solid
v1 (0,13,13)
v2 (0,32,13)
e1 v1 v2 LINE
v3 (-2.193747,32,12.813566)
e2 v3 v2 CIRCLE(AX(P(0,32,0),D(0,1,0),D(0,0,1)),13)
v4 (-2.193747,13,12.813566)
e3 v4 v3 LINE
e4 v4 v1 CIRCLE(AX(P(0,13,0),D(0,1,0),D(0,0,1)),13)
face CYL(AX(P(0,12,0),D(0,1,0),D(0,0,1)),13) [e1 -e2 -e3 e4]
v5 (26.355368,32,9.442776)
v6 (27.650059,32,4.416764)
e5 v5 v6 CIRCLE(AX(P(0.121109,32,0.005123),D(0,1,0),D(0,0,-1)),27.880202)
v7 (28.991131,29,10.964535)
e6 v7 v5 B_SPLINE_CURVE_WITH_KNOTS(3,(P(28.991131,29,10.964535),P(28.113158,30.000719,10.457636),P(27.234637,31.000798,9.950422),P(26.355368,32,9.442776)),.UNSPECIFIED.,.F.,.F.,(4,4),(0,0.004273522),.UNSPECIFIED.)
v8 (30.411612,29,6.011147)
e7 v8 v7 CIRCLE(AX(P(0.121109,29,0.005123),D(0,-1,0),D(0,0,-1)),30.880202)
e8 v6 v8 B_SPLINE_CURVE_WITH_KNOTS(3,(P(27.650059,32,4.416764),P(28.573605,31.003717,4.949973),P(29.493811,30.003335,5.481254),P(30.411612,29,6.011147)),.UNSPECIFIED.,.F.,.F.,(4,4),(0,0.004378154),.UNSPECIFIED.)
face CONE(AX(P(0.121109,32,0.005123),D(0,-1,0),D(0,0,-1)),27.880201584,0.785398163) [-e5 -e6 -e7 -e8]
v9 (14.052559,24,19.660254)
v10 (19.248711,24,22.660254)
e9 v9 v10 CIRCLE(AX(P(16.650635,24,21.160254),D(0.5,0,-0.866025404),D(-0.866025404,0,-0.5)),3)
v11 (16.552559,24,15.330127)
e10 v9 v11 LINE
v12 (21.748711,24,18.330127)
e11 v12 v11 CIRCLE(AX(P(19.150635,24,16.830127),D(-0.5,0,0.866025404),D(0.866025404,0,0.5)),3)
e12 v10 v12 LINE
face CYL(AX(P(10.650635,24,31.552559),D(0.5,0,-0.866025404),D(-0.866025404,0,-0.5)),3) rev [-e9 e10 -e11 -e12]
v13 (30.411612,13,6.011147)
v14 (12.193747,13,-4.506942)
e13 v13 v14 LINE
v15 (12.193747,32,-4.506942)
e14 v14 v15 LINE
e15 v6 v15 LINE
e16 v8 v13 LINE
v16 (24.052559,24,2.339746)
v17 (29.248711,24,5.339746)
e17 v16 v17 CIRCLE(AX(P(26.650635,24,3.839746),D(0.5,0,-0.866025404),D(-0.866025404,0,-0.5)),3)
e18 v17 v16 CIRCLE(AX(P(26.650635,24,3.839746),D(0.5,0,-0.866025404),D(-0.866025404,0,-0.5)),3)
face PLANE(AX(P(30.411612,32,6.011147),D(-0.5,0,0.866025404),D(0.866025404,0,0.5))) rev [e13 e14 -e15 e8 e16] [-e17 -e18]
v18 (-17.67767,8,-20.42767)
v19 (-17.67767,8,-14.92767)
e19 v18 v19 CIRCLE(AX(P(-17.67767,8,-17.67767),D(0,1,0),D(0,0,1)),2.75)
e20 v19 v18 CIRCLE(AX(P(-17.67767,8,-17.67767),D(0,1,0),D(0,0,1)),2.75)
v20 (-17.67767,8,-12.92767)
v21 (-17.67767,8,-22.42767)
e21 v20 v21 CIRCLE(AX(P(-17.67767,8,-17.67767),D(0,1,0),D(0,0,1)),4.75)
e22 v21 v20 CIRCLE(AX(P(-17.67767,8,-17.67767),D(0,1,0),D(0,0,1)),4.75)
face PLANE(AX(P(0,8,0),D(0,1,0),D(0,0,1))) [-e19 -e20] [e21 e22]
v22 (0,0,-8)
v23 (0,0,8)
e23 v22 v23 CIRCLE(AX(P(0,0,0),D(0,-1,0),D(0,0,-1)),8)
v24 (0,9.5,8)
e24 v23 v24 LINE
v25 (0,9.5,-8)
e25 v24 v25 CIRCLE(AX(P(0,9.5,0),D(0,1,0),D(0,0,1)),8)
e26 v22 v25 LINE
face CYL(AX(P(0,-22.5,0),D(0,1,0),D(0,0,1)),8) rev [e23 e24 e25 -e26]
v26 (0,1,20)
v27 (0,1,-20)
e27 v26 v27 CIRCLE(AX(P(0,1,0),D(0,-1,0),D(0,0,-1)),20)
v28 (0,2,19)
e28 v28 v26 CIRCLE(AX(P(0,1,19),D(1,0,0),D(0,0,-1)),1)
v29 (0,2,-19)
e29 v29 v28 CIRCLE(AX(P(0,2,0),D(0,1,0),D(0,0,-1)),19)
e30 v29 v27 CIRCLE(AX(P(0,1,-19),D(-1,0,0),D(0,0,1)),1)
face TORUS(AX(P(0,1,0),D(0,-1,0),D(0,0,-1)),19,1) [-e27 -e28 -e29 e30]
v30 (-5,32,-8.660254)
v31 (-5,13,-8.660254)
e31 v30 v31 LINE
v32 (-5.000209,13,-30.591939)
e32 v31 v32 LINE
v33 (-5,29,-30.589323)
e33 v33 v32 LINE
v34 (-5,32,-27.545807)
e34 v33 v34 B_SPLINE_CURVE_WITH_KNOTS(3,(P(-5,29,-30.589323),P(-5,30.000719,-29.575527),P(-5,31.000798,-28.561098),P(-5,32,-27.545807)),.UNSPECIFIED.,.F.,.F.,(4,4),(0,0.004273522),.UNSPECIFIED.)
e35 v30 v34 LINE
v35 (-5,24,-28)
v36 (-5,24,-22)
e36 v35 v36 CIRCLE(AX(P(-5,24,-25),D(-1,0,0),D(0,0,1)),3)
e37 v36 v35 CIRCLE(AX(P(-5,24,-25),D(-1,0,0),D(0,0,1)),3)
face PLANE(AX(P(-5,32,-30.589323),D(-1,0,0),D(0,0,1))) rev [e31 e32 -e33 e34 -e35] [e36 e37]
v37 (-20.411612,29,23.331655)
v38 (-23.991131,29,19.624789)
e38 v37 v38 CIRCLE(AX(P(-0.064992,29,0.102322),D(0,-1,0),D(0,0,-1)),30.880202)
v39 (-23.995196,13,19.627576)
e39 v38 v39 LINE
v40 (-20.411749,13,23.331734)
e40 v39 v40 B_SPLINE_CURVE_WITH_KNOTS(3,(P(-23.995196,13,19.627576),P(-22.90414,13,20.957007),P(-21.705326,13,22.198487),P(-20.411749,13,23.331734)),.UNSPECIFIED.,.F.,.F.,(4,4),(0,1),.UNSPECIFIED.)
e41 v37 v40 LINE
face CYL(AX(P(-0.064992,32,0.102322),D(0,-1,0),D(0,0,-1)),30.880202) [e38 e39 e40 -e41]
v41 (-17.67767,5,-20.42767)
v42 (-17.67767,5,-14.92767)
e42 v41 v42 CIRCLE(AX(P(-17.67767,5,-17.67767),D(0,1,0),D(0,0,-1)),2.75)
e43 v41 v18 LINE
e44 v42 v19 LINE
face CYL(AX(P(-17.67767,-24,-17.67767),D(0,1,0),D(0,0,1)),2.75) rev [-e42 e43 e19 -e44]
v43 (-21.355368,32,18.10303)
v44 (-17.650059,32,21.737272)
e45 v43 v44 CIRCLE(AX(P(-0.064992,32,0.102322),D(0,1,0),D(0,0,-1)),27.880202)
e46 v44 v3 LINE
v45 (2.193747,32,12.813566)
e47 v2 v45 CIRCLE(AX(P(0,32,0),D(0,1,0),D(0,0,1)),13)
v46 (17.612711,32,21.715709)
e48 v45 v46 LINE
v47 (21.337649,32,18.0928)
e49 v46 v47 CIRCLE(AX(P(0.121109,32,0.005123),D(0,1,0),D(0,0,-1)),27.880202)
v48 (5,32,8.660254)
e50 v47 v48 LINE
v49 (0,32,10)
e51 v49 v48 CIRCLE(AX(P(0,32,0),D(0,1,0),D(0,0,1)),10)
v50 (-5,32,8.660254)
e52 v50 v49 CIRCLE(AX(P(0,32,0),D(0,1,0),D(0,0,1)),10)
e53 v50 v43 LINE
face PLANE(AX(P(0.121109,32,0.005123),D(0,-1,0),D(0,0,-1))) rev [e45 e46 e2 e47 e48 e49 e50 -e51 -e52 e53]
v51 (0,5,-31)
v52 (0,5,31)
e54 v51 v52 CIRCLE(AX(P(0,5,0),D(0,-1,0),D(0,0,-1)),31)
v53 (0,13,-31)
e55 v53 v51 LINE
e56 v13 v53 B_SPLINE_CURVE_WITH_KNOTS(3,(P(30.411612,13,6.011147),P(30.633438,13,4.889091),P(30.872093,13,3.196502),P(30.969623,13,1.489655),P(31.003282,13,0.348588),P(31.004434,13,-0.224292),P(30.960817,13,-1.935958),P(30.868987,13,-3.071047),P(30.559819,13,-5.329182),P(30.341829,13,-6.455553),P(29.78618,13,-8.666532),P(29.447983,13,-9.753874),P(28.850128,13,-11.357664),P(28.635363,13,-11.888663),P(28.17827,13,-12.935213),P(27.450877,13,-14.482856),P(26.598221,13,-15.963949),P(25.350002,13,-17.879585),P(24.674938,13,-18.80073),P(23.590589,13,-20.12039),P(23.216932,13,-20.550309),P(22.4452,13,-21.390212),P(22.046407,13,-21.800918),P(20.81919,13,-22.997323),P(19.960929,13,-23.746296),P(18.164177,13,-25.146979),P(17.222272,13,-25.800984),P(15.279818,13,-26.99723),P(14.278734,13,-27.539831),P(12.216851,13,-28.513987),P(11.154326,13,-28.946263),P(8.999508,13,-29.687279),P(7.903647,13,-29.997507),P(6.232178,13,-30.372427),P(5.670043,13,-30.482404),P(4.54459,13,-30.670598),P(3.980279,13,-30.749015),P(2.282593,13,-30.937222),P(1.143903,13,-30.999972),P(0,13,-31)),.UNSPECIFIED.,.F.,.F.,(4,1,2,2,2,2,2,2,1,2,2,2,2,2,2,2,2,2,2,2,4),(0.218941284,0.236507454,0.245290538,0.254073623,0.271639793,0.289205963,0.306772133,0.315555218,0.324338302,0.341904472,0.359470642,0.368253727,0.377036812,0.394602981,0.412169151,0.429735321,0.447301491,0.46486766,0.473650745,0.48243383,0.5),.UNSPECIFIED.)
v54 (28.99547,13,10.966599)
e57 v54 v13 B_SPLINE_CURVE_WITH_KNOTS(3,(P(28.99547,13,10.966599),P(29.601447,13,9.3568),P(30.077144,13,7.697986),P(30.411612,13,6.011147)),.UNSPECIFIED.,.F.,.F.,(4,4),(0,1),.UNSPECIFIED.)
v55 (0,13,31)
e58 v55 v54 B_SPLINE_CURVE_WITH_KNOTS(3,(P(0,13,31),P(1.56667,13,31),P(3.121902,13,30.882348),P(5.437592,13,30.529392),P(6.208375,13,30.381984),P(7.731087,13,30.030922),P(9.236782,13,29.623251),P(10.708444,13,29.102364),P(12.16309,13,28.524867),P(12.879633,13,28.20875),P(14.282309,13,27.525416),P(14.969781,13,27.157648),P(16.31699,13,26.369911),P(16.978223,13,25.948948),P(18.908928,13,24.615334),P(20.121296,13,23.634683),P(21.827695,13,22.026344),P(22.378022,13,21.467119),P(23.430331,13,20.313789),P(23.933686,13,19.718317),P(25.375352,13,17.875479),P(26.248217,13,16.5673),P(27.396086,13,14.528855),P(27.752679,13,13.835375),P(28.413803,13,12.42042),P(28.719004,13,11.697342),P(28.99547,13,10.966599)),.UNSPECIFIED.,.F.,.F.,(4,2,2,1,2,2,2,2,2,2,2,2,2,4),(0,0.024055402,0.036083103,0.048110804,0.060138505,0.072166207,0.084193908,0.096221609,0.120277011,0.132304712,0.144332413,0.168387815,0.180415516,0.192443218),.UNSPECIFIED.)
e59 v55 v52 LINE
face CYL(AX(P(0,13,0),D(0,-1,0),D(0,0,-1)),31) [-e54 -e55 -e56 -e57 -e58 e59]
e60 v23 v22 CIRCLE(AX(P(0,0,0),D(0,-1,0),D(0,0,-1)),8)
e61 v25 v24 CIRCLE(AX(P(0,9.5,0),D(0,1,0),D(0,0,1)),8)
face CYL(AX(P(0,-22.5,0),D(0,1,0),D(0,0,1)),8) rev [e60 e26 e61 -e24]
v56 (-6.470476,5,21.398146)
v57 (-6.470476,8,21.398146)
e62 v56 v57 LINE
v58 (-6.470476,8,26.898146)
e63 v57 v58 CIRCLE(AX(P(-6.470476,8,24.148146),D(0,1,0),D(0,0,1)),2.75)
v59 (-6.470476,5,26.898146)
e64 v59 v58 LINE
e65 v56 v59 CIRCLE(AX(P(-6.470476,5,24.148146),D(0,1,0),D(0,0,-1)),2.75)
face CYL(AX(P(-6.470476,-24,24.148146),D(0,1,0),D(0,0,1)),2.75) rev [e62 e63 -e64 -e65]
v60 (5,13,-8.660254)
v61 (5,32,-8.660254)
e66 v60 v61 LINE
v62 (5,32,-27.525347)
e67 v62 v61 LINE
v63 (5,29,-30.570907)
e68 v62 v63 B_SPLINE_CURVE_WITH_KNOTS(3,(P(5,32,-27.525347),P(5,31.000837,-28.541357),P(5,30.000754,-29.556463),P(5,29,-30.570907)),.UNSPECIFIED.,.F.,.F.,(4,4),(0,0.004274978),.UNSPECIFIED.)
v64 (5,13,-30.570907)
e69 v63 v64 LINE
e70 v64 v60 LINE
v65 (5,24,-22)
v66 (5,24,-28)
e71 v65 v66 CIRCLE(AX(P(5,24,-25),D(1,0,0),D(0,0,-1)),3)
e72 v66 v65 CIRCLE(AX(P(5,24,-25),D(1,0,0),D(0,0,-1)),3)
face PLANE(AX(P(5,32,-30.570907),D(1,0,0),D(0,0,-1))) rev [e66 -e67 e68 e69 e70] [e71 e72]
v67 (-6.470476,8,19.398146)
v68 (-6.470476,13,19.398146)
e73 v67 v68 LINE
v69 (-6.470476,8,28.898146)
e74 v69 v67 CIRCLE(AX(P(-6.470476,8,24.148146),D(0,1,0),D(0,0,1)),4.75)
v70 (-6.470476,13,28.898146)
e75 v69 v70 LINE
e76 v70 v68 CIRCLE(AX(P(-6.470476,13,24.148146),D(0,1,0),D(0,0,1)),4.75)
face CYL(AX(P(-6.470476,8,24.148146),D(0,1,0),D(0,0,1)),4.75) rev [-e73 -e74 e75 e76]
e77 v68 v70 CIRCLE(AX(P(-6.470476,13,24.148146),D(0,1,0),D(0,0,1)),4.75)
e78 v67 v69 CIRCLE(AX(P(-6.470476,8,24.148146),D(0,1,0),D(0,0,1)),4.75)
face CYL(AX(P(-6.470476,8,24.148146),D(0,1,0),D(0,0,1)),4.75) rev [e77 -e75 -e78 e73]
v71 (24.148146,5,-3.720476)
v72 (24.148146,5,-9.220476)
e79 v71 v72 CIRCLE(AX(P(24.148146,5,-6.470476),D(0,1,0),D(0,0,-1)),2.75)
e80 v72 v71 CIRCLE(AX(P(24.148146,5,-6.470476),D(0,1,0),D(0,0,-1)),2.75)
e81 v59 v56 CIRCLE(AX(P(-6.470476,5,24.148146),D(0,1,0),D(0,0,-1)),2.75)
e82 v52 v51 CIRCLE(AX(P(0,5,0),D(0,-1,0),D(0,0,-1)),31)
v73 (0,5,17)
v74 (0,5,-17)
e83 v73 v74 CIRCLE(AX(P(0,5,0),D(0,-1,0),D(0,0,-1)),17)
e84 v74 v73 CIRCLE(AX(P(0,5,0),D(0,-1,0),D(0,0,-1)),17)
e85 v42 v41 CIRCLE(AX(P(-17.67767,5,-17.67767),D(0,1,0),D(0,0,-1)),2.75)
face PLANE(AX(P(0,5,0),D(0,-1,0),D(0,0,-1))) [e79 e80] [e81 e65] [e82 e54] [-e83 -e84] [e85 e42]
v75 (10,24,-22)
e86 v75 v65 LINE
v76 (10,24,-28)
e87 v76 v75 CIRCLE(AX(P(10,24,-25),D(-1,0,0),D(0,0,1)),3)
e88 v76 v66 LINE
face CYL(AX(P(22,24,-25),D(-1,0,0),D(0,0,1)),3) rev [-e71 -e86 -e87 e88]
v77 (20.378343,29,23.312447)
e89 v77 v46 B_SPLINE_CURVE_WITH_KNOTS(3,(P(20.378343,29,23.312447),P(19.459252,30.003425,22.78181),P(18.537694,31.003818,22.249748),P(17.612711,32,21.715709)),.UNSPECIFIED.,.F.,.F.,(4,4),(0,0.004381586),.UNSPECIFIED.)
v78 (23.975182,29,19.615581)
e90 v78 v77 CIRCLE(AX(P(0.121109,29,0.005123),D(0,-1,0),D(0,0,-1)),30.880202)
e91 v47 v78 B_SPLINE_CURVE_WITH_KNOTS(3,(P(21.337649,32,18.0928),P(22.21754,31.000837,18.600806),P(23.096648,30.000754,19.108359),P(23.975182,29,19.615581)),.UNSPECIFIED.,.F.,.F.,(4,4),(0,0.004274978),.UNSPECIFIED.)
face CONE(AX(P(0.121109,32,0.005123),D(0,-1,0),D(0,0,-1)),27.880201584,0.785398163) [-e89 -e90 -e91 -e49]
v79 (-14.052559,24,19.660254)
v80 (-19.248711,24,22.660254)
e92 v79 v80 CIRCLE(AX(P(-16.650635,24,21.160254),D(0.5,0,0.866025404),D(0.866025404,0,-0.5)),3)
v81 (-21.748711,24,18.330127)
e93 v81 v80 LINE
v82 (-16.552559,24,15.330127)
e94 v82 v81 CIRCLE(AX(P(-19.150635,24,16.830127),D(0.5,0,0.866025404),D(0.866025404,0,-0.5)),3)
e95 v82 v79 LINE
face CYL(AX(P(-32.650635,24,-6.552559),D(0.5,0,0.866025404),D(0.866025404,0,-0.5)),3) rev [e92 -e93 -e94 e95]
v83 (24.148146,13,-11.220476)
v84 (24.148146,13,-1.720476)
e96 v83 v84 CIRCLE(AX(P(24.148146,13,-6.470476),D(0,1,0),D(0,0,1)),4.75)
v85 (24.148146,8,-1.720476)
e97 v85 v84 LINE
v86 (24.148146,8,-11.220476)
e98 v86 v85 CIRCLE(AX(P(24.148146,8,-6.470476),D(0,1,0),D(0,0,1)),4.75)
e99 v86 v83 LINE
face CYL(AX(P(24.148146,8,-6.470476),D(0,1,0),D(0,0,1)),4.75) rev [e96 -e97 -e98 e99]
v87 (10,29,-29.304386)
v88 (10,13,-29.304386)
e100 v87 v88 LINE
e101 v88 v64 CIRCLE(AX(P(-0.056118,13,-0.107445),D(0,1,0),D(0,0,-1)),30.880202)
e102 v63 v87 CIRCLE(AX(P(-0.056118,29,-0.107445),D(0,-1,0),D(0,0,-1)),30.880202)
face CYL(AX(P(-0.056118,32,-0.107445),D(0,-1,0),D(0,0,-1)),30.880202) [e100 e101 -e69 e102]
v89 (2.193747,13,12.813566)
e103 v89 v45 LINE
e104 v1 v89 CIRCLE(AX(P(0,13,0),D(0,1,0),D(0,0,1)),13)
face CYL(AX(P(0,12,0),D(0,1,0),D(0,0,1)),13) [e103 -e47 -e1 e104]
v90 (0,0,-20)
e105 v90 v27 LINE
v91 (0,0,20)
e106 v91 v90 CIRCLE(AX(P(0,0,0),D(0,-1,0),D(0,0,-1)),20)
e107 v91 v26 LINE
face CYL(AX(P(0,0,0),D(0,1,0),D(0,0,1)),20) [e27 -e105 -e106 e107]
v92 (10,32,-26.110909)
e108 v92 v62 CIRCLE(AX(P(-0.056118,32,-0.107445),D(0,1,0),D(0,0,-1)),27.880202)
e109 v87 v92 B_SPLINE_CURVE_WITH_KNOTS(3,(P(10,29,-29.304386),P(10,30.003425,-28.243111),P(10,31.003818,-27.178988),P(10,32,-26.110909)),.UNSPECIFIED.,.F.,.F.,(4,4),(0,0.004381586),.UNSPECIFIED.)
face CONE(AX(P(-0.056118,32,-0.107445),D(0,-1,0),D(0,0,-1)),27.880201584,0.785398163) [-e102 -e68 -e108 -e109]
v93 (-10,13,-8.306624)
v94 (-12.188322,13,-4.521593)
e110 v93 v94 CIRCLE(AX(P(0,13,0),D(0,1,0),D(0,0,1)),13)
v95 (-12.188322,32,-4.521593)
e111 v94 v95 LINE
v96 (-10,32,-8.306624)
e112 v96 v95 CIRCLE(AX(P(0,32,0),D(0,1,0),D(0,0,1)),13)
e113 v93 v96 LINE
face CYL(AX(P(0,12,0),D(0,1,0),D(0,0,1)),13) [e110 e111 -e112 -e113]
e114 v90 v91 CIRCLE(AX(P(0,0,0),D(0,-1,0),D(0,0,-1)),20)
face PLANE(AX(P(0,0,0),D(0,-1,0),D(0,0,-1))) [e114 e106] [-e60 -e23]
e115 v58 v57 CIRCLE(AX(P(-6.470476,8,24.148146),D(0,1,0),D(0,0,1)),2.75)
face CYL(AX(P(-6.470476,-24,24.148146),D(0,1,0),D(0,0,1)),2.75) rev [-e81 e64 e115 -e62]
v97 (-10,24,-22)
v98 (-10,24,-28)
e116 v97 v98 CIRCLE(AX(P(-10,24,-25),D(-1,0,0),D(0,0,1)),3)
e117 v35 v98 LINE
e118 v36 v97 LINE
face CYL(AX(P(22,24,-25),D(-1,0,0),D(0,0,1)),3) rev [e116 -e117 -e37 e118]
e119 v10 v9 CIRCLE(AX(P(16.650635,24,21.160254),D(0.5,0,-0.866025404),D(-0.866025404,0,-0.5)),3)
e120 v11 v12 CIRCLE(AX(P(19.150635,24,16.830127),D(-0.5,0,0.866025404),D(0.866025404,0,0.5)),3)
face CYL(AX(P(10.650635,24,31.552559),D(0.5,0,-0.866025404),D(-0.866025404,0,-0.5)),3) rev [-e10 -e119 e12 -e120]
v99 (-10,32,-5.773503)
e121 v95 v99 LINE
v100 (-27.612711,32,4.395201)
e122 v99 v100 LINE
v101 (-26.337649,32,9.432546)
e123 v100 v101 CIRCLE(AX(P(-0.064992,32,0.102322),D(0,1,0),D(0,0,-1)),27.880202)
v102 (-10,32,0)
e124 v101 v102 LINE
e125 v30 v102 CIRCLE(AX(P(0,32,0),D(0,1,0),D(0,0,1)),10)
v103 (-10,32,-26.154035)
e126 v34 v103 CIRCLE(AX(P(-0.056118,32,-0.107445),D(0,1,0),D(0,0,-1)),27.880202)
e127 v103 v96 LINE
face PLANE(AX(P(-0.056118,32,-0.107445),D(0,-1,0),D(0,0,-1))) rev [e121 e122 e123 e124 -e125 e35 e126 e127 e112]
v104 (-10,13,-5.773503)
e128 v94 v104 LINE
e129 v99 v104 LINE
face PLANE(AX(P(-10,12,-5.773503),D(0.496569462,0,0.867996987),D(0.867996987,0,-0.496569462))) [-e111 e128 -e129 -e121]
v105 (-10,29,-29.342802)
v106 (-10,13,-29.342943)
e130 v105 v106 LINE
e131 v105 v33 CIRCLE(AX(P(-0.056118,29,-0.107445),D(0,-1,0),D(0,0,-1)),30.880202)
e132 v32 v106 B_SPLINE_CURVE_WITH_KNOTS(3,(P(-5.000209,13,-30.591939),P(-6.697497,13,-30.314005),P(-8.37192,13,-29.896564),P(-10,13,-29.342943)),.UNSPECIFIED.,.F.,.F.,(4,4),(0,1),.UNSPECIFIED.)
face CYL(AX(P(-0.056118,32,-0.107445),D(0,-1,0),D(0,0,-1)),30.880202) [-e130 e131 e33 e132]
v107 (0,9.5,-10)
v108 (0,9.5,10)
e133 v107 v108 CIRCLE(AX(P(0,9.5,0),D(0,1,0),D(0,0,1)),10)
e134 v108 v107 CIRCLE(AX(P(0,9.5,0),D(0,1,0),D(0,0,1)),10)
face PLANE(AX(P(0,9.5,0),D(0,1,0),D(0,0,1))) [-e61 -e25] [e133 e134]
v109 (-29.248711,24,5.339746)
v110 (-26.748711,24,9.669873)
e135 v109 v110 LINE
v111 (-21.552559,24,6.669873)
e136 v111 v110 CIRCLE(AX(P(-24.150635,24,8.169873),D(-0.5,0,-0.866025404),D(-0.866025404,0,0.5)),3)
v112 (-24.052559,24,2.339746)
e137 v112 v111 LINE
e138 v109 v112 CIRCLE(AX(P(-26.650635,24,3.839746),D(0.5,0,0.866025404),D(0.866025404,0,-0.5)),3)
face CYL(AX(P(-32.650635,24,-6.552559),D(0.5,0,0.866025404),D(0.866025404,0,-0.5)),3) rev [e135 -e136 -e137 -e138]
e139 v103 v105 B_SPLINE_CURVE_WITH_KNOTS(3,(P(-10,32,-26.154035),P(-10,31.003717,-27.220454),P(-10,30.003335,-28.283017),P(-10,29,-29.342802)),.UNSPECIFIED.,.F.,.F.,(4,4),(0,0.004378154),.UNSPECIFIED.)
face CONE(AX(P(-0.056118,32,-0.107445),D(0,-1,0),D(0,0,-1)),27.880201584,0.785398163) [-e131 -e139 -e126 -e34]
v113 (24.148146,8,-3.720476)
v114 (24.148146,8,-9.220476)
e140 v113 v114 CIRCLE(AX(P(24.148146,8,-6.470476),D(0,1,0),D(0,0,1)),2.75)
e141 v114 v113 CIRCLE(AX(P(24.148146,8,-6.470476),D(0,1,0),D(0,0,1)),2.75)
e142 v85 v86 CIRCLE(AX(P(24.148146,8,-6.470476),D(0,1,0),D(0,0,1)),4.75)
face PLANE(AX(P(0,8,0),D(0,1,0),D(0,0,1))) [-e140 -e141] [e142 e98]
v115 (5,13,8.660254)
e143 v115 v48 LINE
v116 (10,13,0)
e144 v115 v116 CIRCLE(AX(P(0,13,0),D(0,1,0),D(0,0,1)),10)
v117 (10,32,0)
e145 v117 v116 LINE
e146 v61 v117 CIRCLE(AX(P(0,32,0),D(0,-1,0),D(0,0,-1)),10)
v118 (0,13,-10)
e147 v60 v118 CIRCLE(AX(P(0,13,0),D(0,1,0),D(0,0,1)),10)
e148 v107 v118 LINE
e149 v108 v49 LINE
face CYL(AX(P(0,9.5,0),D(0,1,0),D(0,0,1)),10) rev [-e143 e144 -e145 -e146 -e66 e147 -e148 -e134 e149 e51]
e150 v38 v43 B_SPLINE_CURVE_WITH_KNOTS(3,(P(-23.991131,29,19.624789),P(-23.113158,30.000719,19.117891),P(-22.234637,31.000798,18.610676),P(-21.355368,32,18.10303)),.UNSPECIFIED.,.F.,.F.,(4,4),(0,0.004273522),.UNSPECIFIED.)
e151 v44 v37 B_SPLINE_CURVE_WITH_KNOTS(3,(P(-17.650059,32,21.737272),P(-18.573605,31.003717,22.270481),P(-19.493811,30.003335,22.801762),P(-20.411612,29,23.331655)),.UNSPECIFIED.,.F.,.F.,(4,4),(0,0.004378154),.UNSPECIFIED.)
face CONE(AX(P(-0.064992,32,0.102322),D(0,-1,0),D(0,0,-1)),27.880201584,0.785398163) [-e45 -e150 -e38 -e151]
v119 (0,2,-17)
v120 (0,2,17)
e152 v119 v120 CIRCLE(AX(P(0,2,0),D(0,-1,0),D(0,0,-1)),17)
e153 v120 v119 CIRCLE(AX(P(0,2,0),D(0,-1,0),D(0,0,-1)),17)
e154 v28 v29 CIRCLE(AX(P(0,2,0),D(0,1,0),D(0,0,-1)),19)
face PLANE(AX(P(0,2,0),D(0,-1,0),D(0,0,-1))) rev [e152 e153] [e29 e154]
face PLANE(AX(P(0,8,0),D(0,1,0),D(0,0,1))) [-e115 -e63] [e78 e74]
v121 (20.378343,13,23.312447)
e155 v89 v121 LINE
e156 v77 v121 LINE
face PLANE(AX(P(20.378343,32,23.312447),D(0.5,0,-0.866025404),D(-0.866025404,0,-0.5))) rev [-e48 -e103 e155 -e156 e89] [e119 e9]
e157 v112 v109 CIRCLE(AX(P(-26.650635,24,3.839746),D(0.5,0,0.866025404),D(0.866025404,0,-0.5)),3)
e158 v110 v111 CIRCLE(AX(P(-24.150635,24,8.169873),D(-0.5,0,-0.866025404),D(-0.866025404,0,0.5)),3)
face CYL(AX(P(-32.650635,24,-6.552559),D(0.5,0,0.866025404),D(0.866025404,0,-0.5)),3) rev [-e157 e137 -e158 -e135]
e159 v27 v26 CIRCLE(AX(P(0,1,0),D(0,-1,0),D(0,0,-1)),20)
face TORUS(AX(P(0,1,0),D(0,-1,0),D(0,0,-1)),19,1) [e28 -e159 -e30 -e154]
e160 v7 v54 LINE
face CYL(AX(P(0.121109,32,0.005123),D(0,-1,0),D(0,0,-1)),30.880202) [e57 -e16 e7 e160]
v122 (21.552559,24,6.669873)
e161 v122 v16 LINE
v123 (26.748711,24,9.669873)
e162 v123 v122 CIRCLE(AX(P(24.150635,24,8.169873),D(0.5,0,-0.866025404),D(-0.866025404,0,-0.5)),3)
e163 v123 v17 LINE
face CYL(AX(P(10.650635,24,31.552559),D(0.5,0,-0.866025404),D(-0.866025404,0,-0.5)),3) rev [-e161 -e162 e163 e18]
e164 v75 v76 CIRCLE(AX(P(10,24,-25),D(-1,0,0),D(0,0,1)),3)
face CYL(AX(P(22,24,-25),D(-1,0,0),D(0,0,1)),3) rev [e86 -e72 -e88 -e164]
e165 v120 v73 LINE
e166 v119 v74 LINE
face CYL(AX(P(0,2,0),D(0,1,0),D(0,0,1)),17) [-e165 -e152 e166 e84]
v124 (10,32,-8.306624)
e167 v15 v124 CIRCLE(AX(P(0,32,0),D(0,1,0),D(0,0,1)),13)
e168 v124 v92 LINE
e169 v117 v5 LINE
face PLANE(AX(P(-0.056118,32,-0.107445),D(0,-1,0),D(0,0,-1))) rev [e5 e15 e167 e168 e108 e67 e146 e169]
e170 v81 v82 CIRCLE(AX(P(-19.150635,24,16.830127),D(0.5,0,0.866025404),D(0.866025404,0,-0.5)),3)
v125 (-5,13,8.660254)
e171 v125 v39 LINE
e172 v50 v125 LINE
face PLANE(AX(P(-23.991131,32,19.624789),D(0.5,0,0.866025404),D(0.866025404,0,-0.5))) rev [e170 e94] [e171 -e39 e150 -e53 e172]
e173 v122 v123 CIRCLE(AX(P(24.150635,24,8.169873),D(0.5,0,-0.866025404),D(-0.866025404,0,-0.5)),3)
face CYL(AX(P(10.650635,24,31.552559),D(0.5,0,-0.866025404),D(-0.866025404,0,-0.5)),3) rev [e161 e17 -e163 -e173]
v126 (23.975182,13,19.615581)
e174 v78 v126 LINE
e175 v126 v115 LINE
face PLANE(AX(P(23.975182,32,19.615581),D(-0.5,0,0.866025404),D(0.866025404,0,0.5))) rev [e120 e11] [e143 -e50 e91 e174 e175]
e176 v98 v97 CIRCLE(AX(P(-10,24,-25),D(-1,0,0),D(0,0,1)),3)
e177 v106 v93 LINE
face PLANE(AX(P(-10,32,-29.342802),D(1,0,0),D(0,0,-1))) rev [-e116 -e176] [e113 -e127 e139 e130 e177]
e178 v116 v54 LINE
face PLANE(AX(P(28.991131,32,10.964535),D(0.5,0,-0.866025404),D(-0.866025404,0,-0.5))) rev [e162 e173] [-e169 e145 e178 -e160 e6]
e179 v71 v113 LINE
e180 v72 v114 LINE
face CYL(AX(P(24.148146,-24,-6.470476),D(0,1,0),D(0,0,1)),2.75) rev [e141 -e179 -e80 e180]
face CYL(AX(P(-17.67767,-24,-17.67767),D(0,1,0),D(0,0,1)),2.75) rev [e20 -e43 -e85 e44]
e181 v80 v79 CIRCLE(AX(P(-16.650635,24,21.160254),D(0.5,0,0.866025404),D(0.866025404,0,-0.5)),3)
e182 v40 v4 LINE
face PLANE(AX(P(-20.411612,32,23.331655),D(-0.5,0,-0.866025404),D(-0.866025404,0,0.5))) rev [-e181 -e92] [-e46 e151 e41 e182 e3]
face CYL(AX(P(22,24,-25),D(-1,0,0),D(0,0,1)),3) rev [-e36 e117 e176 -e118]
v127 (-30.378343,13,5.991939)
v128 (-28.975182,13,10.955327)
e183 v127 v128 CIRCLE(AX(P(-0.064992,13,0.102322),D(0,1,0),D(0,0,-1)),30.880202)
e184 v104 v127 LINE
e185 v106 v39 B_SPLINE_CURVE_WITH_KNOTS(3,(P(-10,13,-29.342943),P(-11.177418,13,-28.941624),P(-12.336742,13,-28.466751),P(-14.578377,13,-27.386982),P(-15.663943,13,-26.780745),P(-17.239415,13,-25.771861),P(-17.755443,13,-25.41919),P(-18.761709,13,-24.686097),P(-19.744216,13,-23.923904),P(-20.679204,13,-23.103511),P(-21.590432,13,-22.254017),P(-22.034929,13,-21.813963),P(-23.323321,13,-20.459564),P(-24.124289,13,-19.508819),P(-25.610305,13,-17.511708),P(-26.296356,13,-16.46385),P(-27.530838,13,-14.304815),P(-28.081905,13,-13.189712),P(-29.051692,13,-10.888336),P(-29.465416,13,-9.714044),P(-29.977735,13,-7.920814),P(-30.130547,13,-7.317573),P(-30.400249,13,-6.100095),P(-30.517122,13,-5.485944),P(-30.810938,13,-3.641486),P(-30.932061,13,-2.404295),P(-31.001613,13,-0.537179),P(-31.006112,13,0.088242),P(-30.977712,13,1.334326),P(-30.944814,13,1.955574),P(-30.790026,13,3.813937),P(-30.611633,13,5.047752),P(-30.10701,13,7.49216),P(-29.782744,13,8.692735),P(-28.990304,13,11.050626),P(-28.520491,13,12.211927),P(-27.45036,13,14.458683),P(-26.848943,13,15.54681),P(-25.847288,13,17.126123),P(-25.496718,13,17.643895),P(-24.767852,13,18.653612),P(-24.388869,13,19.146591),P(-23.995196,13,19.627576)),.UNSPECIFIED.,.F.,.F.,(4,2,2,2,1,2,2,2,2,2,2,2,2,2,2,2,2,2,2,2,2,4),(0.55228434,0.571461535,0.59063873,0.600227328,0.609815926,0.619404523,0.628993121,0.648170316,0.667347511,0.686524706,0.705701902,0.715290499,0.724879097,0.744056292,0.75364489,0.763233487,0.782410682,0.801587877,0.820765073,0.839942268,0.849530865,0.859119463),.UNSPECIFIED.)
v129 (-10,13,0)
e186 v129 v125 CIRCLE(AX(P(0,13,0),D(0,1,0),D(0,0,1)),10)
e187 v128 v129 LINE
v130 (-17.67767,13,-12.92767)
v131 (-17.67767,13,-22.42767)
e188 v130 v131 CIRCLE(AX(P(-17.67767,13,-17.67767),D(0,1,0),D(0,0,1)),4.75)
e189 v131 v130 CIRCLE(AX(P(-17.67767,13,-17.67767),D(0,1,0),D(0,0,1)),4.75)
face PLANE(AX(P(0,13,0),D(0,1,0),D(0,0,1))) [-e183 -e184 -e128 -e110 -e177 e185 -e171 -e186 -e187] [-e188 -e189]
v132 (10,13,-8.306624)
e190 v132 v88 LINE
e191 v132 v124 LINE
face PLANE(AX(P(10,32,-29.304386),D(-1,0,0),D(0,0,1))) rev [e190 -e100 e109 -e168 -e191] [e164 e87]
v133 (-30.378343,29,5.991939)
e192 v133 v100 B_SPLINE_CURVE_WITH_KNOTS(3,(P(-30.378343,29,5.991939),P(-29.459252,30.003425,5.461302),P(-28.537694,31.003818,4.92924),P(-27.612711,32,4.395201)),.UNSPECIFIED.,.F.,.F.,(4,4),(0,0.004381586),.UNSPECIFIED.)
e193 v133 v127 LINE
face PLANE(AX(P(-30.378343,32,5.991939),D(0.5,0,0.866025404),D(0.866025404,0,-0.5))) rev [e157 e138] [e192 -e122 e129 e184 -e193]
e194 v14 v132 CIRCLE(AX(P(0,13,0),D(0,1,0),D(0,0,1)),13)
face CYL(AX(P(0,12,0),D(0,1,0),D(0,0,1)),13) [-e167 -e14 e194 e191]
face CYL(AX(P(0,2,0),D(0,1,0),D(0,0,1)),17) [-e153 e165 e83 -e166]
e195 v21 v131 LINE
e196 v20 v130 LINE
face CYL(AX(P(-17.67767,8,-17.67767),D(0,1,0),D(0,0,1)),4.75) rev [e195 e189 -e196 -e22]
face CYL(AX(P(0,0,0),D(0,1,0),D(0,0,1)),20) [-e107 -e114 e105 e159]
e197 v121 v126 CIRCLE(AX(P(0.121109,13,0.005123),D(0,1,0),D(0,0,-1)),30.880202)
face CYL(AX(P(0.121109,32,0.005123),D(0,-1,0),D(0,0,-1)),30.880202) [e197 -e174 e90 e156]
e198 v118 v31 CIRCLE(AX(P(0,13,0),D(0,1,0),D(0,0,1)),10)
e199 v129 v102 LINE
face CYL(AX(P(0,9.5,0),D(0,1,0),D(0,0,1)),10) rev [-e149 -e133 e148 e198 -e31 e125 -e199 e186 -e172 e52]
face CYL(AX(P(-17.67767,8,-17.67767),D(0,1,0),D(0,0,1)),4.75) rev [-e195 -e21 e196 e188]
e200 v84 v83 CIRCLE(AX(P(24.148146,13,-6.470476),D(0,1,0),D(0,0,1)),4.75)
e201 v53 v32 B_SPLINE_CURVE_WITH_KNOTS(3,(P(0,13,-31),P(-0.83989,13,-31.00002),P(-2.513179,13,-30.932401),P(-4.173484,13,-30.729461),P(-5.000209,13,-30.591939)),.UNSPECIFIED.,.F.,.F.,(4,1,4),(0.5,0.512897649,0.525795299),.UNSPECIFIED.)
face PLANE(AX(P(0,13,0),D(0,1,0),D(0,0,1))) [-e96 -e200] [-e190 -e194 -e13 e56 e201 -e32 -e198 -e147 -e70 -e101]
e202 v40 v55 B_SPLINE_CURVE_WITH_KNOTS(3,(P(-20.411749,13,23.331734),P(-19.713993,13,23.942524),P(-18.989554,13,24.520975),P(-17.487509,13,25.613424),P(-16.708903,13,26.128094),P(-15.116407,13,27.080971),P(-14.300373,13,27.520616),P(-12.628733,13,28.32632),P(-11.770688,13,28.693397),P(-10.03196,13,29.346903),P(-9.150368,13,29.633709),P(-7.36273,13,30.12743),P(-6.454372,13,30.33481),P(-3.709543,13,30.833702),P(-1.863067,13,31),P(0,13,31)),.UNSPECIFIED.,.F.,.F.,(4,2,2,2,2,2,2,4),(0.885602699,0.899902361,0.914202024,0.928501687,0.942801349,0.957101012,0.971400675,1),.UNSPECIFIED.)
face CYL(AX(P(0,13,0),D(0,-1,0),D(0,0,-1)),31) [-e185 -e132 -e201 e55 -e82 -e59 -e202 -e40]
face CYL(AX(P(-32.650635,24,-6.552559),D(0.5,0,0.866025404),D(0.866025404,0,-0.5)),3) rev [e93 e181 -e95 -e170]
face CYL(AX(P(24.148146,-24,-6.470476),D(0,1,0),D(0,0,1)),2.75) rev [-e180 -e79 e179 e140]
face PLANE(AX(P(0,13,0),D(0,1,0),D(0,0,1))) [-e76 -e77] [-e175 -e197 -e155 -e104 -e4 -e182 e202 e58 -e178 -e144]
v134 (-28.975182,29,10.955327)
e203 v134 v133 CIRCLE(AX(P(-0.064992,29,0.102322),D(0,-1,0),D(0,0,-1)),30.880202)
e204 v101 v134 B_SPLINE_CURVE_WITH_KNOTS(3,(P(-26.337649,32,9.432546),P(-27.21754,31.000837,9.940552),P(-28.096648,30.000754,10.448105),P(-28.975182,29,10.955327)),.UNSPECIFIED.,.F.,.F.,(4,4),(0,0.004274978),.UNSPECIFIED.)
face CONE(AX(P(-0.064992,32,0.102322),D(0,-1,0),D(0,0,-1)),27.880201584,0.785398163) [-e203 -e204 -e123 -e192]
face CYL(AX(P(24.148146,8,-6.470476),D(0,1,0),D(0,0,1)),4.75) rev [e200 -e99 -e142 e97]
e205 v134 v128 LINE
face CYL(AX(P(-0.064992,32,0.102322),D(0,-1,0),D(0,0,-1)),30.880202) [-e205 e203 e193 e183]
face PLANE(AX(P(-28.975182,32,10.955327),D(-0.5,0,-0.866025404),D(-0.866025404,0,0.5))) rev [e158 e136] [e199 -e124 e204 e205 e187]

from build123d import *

# Parameters (mm, degrees)
BASE_DISC_SKETCH_R             = 31
BASE_DISC_62_DEPTH             = 13
CLAMP_ARMS_DEPTH               = 19
CENTRE_BORE_SKETCH_R           = 10
CENTRE_BORE_DEPTH              = 22.5
CENTRE_HUB_DEPTH               = 20
MOUNTING_COUNTERBORES_SKETCH_R = 4.75
MOUNTING_COUNTERBORES_DEPTH    = 5
ARM_CROSS_HOLE_1_SKETCH_R      = 3
ARM_CROSS_HOLE_1_DEPTH         = 32
ARM_CROSS_HOLE_2_SKETCH_R      = 3
ARM_CROSS_HOLE_2_DEPTH         = 32
ARM_CROSS_HOLE_3_SKETCH_R      = 3
ARM_CROSS_HOLE_3_DEPTH         = 32
MOUNTING_HOLES_SKETCH_R        = 2.75
MOUNTING_HOLES_3X_DEPTH        = 32
CENTRE_THROUGH_BORE_SKETCH_R   = 8
CENTRE_THROUGH_BORE_DEPTH      = 32
ARM_CHAMFER_1_SIZE             = 3
ARM_CHAMFER_2_SIZE             = 3
ARM_CHAMFER_3_SIZE             = 3
ARM_CHAMFER_4_SIZE             = 3
ARM_CHAMFER_5_SIZE             = 3
ARM_CHAMFER_6_SIZE             = 3
BOTTOM_RECESS_SKETCH_R         = 31
BOTTOM_RECESS_DEPTH            = 5
RECESS_RING_SKETCH_R           = 17
RECESS_RING_DEPTH              = 3
LOCATING_LIP_SKETCH_R          = 20
LOCATING_LIP_DEPTH             = 2
LOCATING_LIP_FILLET_R1_R       = 1
LIP_BORE_SKETCH_R              = 8
LIP_BORE_DEPTH                 = 19


with BuildPart() as part:
    # Base Disc Sketch → Base Disc Ø62 (new body)
    with BuildSketch(Plane(origin=(0, 0, 0), x_dir=(1, 0, 0), z_dir=(0, 1, 0))):
        with Locations(Location((0, 0, 0), (0, 0, 90))):
            Circle(BASE_DISC_SKETCH_R)
    extrude(amount=BASE_DISC_62_DEPTH)

    # Clamp Arms Sketch → Clamp Arms (add)
    with BuildSketch(Plane(origin=(0, 13, 0), x_dir=(1, 0, 0), z_dir=(0, 1, 0))):
        with BuildLine():
            Line((10, 29.304386049), (10, 5.773502692))
            Line((10, 5.773502692), (30.411611519, -6.011146713))
            ThreePointArc((30.411611519, -6.011146713), (29.804874358, -8.517522175), (28.991130921, -10.96453455))
            Line((28.991130921, -10.96453455), (5, 2.886751346))
            Line((5, 2.886751346), (5, 30.570907429))
            ThreePointArc((5, 30.570907429), (7.526489622, 30.042223032), (10, 29.304386049))
        make_face()
        with BuildLine():
            Line((-10, 29.342801502), (-10, 5.773502692))
            Line((-10, 5.773502692), (-30.378342761, -5.991938987))
            ThreePointArc((-30.378342761, -5.991938987), (-29.780573143, -8.502980302), (-28.97518245, -10.955326696))
            Line((-28.97518245, -10.955326696), (-5, 2.886751346))
            Line((-5, 2.886751346), (-5, 30.589323137))
            ThreePointArc((-5, 30.589323137), (-7.526046598, 30.070539438), (-10, 29.342801502))
        make_face()
        with BuildLine():
            Line((23.97518245, -19.615580733), (0, -5.773502692))
            Line((0, -5.773502692), (-23.991130921, -19.624788587))
            ThreePointArc((-23.991130921, -19.624788587), (-22.27882776, -21.553017263), (-20.411611519, -23.331654789))
            Line((-20.411611519, -23.331654789), (0, -11.547005384))
            Line((0, -11.547005384), (20.378342761, -23.312447062))
            ThreePointArc((20.378342761, -23.312447062), (22.254083521, -21.53924273), (23.97518245, -19.615580733))
        make_face()
    extrude(amount=CLAMP_ARMS_DEPTH)

    # Centre Bore Sketch → Centre Bore (cut)
    with BuildSketch(Plane(origin=(0, 32, 0), x_dir=(1, 0, 0), z_dir=(0, 1, 0))):
        with Locations(Location((0, 0, 0), (0, 0, 270))):
            Circle(CENTRE_BORE_SKETCH_R)
    extrude(amount=-CENTRE_BORE_DEPTH, mode=Mode.SUBTRACT)

    # Centre Hub Sketch → Centre Hub (add)
    with BuildSketch(Plane(origin=(0, 32, 0), x_dir=(1, 0, 0), z_dir=(0, 1, 0))):
        with BuildLine():
            Line((-10, 8.306623863), (-10, 5.773502692))
            Line((-10, 5.773502692), (-12.188322207, 4.521592837))
            ThreePointArc((-12.188322207, 4.521592837), (-11.254422489, 6.506763746), (-10, 8.306623863))
        make_face()
        with BuildLine():
            Line((10, 8.306623863), (10, 5.773502692))
            Line((10, 5.773502692), (12.193747285, 4.506942106))
            ThreePointArc((12.193747285, 4.506942106), (11.258330249, 6.5), (10, 8.306623863))
        make_face()
        with BuildLine():
            Line((-2.193747285, -12.813565969), (0, -11.547005384))
            Line((0, -11.547005384), (2.193747285, -12.813565969))
            ThreePointArc((2.193747285, -12.813565969), (0, -13), (-2.193747285, -12.813565969))
        make_face()
    extrude(amount=-CENTRE_HUB_DEPTH)

    # Mounting Counterbores Sketch → Mounting Counterbores (cut)
    with BuildSketch(Plane(origin=(0, 13, 0), x_dir=(1, 0, 0), z_dir=(0, 1, 0))):
        with Locations(Location((-6.470476128, -24.148145657, 0), (0, 0, 270))):
            Circle(MOUNTING_COUNTERBORES_SKETCH_R)
        with Locations(Location((24.148145657, 6.470476128, 0), (0, 0, 270))):
            Circle(MOUNTING_COUNTERBORES_SKETCH_R)
        with Locations(Location((-17.67766953, 17.67766953, 0), (0, 0, 270))):
            Circle(MOUNTING_COUNTERBORES_SKETCH_R)
    extrude(amount=-MOUNTING_COUNTERBORES_DEPTH, mode=Mode.SUBTRACT)

    # Arm Cross Hole 1 Sketch → Arm Cross Hole 1 (cut)
    with BuildSketch(Plane.ZY.offset(10)):
        with Locations((-25, 24)):
            Circle(ARM_CROSS_HOLE_1_SKETCH_R)
    extrude(amount=-ARM_CROSS_HOLE_1_DEPTH, mode=Mode.SUBTRACT)

    # Arm Cross Hole 2 Sketch → Arm Cross Hole 2 (cut)
    with BuildSketch(Plane(origin=(5, 0, -8.660254038), x_dir=(-0.8660254037844363, 0, -0.5000000000000043), z_dir=(0.5000000000000042, 0, -0.8660254037844362))):
        with Locations((-25, 24)):
            Circle(ARM_CROSS_HOLE_2_SKETCH_R)
    extrude(amount=-ARM_CROSS_HOLE_2_DEPTH, mode=Mode.SUBTRACT)

    # Arm Cross Hole 3 Sketch → Arm Cross Hole 3 (cut)
    with BuildSketch(Plane(origin=(5, 0, 8.660254038), x_dir=(0.8660254037844433, 0, -0.4999999999999921), z_dir=(0.49999999999999206, 0, 0.8660254037844431))):
        with Locations((-25, 24)):
            Circle(ARM_CROSS_HOLE_3_SKETCH_R)
    extrude(amount=-ARM_CROSS_HOLE_3_DEPTH, mode=Mode.SUBTRACT)

    # Mounting Holes Sketch → Mounting Holes 3x (cut)
    with BuildSketch(Plane(origin=(0, 8, 0), x_dir=(1, 0, 0), z_dir=(0, 1, 0))):
        with Locations(Location((-17.67766953, 17.67766953, 0), (0, 0, 270))):
            Circle(MOUNTING_HOLES_SKETCH_R)
        with Locations(Location((24.148145657, 6.470476128, 0), (0, 0, 270))):
            Circle(MOUNTING_HOLES_SKETCH_R)
        with Locations(Location((-6.470476128, -24.148145657, 0), (0, 0, 270))):
            Circle(MOUNTING_HOLES_SKETCH_R)
    extrude(amount=-MOUNTING_HOLES_3X_DEPTH, mode=Mode.SUBTRACT)

    # Centre Through Bore Sketch → Centre Through Bore (cut)
    with BuildSketch(Plane(origin=(0, 9.5, 0), x_dir=(1, 0, 0), z_dir=(0, 1, 0))):
        with Locations(Location((0, 0, 0), (0, 0, 270))):
            Circle(CENTRE_THROUGH_BORE_SKETCH_R)
    extrude(amount=-CENTRE_THROUGH_BORE_DEPTH, mode=Mode.SUBTRACT)

    # Arm Chamfer 1
    arm_chamfer_1_edges = [part.edges().sort_by_distance(p)[0] for p in [
        (-29.780573143, 32, 8.502980302),
    ]]
    chamfer(arm_chamfer_1_edges, length=ARM_CHAMFER_1_SIZE)

    # Arm Chamfer 2
    arm_chamfer_2_edges = [part.edges().sort_by_distance(p)[0] for p in [
        (-22.27882776, 32, 21.553017263),
    ]]
    chamfer(arm_chamfer_2_edges, length=ARM_CHAMFER_2_SIZE)

    # Arm Chamfer 3
    arm_chamfer_3_edges = [part.edges().sort_by_distance(p)[0] for p in [
        (22.254083521, 32, 21.53924273),
    ]]
    chamfer(arm_chamfer_3_edges, length=ARM_CHAMFER_3_SIZE)

    # Arm Chamfer 4
    arm_chamfer_4_edges = [part.edges().sort_by_distance(p)[0] for p in [
        (29.804874358, 32, 8.517522175),
    ]]
    chamfer(arm_chamfer_4_edges, length=ARM_CHAMFER_4_SIZE)

    # Arm Chamfer 5
    arm_chamfer_5_edges = [part.edges().sort_by_distance(p)[0] for p in [
        (7.526489622, 32, -30.042223032),
    ]]
    chamfer(arm_chamfer_5_edges, length=ARM_CHAMFER_5_SIZE)

    # Arm Chamfer 6
    arm_chamfer_6_edges = [part.edges().sort_by_distance(p)[0] for p in [
        (-7.526046598, 32, -30.070539438),
    ]]
    chamfer(arm_chamfer_6_edges, length=ARM_CHAMFER_6_SIZE)

    # Bottom Recess Sketch → Bottom Recess (cut)
    with BuildSketch(Plane.XZ):
        with Locations(Location((0, 0, 0), (0, 0, 270))):
            Circle(BOTTOM_RECESS_SKETCH_R)
    extrude(amount=-BOTTOM_RECESS_DEPTH, mode=Mode.SUBTRACT)

    # Recess Ring Sketch → Recess Ring (add)
    with BuildSketch(Plane.XZ.offset(-5)):
        with Locations(Location((0, 0, 0), (0, 0, 270))):
            Circle(RECESS_RING_SKETCH_R)
    extrude(amount=RECESS_RING_DEPTH)

    # Locating Lip Sketch → Locating Lip (add)
    with BuildSketch(Plane.XZ.offset(-2)):
        with Locations(Location((0, 0, 0), (0, 0, 270))):
            Circle(LOCATING_LIP_SKETCH_R)
    extrude(amount=LOCATING_LIP_DEPTH)

    # Locating Lip Fillet R1
    locating_lip_fillet_r1_edges = [part.edges().sort_by_distance(p)[0] for p in [
        (0, 2, 20),
    ]]
    fillet(locating_lip_fillet_r1_edges, radius=LOCATING_LIP_FILLET_R1_R)

    # Lip Bore Sketch → Lip Bore (cut)
    with BuildSketch(Plane(origin=(0, 5, 0), x_dir=(1, 0, 0), z_dir=(0, 1, 0))):
        with Locations(Location((0, 0, 0), (0, 0, 270))):
            Circle(LIP_BORE_SKETCH_R)
    extrude(amount=-LIP_BORE_DEPTH, mode=Mode.SUBTRACT)


solid = part.part
